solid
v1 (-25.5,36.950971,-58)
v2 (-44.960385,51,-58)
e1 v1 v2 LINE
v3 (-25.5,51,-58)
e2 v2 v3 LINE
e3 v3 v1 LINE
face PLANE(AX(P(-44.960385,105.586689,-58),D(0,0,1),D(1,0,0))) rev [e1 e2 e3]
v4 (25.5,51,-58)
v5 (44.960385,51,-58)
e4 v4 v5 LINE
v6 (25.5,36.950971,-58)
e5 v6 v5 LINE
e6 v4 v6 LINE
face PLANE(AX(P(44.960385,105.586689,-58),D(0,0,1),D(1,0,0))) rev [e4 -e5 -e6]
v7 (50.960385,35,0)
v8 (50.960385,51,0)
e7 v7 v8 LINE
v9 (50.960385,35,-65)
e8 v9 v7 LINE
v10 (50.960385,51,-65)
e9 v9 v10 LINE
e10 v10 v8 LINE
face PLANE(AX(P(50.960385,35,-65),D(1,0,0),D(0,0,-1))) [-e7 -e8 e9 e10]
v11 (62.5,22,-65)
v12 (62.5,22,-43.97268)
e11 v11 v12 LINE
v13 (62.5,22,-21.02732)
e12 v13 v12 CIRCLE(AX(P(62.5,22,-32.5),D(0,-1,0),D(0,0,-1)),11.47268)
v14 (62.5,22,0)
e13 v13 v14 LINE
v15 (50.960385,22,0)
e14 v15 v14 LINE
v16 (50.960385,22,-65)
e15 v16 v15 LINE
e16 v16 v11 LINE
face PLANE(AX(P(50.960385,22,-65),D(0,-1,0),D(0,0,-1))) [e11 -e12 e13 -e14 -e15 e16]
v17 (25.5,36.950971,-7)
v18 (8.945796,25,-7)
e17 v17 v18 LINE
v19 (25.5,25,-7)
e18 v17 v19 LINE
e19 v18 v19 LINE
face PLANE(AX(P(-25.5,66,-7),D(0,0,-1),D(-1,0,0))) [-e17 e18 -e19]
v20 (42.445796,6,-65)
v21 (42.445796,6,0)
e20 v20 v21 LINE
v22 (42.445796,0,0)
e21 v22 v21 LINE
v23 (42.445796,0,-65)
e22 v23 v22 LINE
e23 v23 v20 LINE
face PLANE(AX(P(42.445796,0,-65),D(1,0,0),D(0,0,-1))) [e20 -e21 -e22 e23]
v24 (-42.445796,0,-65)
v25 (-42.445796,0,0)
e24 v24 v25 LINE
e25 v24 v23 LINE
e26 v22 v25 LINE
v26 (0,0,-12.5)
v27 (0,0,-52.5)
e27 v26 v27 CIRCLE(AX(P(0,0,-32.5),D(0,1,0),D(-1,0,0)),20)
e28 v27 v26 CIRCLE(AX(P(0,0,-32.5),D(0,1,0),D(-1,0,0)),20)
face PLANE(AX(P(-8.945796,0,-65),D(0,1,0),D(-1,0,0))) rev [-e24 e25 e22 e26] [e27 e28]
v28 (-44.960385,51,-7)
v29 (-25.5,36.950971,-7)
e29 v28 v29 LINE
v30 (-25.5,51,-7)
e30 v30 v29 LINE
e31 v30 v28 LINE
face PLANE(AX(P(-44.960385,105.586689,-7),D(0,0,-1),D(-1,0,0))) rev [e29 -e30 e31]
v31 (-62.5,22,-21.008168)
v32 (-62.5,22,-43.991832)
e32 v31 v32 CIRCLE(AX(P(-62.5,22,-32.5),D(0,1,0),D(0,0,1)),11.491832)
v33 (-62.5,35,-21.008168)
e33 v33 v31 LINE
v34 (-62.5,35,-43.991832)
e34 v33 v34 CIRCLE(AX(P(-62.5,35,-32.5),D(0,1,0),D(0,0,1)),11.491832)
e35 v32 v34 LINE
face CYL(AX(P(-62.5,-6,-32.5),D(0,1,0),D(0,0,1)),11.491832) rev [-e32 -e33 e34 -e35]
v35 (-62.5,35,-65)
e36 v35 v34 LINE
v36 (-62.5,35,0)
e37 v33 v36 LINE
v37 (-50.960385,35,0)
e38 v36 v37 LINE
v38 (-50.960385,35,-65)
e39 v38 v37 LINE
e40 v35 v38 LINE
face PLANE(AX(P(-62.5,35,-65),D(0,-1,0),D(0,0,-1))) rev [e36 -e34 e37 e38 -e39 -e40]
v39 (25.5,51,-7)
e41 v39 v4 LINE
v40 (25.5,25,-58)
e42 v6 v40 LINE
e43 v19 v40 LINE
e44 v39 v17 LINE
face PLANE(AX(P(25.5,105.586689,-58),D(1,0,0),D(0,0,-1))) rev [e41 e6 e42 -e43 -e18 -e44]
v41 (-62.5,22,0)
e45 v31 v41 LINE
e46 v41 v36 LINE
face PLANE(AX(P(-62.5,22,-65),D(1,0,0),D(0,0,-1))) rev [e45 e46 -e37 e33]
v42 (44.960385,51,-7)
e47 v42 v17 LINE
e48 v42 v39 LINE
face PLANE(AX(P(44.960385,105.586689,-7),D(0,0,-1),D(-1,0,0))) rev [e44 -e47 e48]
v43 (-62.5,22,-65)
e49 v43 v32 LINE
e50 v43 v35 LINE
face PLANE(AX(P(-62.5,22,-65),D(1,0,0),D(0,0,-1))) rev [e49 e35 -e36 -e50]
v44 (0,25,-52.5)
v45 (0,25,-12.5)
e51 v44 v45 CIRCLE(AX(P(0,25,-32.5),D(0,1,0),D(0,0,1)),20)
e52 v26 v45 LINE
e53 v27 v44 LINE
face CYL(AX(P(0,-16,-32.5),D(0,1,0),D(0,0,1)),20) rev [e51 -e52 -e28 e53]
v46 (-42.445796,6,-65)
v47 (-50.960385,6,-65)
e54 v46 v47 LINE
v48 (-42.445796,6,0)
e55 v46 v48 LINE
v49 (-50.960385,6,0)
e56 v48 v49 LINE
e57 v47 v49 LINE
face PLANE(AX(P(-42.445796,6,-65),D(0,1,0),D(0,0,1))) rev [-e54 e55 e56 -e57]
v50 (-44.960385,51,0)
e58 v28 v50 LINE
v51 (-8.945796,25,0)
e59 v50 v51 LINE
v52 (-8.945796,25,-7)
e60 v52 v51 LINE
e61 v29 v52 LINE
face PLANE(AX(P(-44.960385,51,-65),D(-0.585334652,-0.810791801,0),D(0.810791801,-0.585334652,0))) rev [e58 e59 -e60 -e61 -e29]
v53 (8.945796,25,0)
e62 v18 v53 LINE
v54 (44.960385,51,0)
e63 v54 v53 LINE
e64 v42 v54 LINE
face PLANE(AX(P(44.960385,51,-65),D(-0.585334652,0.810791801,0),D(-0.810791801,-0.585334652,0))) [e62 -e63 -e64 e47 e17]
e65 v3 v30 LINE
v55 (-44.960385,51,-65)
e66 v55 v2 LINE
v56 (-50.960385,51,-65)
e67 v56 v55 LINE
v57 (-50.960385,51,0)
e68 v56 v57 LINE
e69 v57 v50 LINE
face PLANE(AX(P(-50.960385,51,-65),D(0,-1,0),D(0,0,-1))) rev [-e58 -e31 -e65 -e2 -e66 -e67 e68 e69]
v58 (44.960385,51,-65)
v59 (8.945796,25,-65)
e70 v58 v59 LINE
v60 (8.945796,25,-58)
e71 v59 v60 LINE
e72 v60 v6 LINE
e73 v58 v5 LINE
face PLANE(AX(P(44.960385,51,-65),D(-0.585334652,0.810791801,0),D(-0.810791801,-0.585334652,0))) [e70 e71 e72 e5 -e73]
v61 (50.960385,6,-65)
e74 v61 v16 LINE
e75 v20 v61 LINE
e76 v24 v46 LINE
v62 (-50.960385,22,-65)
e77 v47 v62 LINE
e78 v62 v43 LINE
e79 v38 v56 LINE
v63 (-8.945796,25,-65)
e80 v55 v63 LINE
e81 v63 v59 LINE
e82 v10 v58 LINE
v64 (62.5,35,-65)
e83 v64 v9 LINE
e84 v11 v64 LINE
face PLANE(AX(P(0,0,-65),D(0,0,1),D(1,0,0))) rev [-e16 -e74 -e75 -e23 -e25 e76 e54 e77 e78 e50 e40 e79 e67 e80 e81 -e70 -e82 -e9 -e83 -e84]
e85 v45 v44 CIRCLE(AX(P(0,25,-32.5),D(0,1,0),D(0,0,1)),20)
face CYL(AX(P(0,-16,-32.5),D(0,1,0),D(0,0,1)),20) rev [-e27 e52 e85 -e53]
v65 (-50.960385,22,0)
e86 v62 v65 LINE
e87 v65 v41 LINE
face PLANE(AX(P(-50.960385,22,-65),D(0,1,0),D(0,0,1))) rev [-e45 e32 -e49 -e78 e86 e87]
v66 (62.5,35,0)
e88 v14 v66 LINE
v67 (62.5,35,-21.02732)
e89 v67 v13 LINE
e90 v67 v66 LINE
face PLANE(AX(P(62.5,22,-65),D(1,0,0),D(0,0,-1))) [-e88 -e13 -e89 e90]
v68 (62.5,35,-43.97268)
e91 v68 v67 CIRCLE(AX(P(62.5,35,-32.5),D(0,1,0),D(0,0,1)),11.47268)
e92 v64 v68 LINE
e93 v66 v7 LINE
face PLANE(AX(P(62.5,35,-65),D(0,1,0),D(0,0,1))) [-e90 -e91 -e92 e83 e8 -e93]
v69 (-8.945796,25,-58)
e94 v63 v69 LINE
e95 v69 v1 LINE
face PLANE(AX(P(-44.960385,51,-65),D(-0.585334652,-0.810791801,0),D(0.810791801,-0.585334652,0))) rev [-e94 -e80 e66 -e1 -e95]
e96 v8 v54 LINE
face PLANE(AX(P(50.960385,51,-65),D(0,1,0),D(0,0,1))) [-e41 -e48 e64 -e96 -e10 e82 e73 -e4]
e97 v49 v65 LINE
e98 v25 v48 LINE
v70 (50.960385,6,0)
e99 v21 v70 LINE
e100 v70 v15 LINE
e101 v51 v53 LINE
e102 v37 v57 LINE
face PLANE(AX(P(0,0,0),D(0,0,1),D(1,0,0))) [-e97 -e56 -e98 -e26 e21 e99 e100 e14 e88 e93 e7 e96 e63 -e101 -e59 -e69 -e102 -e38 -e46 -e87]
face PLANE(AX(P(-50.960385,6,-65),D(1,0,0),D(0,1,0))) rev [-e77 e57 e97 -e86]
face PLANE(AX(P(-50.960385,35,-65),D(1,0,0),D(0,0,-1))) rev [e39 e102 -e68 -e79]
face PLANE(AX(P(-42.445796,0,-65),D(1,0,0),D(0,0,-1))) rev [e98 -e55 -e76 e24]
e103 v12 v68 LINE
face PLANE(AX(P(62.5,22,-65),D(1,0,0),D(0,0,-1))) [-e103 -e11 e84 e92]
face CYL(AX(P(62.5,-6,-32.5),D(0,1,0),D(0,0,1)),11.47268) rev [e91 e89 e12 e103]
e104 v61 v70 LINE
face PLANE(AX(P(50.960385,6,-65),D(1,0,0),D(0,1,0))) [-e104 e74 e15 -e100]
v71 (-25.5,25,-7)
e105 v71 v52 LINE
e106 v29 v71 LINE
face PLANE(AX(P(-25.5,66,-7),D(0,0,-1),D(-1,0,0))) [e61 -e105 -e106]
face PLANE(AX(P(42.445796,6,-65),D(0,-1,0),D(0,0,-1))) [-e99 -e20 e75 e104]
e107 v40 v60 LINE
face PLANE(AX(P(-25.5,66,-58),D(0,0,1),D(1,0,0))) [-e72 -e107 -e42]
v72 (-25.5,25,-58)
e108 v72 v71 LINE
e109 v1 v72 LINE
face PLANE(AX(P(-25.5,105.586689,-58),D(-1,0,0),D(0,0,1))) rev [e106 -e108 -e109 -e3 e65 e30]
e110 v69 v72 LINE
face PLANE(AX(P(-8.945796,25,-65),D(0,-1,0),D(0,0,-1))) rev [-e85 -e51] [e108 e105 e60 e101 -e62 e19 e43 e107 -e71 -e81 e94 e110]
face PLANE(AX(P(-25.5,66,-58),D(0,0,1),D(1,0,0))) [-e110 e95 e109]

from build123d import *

# Parameters (mm, degrees)
STEPPED_CRADLE_BLOCK_65_DEPTH = 65
RAISED_BOSS_SKETCH_W          = 19.460384675
RAISED_BOSS_SKETCH_H          = 51
RAISED_BOSS_DEPTH             = 26
CRADLE_SLOT_SKETCH_W          = 51
CRADLE_SLOT_SKETCH_H          = 51
CRADLE_SLOT_CUT_DEPTH         = 41
CENTER_HOLE_SKETCH_R          = 20
CENTER_HOLE_40_DEPTH          = 41
FRONT_RELIEF_SKETCH_R         = 11.472679984
FRONT_RELIEF_SKETCH_R_2       = 11.491831568
FRONT_RELIEF_CUT_DEPTH        = 41


with BuildPart() as part:
    # Stepped Cradle Profile Sketch → Stepped Cradle Block 65 (new body)
    with BuildSketch(Plane.XY):
        Polygon((-42.445795816, 0), (-42.445795816, 6), (-50.960384675, 6), (-50.960384675, 22), (-62.5, 22), (-62.5, 35), (-50.960384675, 35), (-50.960384675, 51), (-44.960384675, 51), (-8.945795816, 25), (8.945795816, 25), (44.960384675, 51), (50.960384675, 51), (50.960384675, 35), (62.5, 35), (62.5, 22), (50.960384675, 22), (50.960384675, 6), (42.445795816, 6), (42.445795816, 0), (8.945795816, 0), (-8.945795816, 0), align=None)
    extrude(amount=-STEPPED_CRADLE_BLOCK_65_DEPTH)

    # Raised Boss Sketch → Raised Boss (add)
    with BuildSketch(Plane(origin=(0, 25, 0), x_dir=(1, 0, 0), z_dir=(0, 1, 0))):
        with Locations((-35.230192338, 32.5)):
            Rectangle(RAISED_BOSS_SKETCH_W, RAISED_BOSS_SKETCH_H)
        with Locations((35.230192338, 32.5)):
            Rectangle(RAISED_BOSS_SKETCH_W, RAISED_BOSS_SKETCH_H)
    extrude(amount=RAISED_BOSS_DEPTH)

    # Cradle Slot Sketch → Cradle Slot Cut (cut)
    with BuildSketch(Plane(origin=(0, 25, 0), x_dir=(1, 0, 0), z_dir=(0, 1, 0))):
        with Locations((0, 32.5)):
            Rectangle(CRADLE_SLOT_SKETCH_W, CRADLE_SLOT_SKETCH_H)
    extrude(amount=CRADLE_SLOT_CUT_DEPTH, mode=Mode.SUBTRACT)

    # Center Hole Sketch → Center Hole Ø40 (cut)
    with BuildSketch(Plane(origin=(0, 25, 0), x_dir=(1, 0, 0), z_dir=(0, 1, 0))):
        with Locations(Location((0, 32.5, 0), (0, 0, 270))):
            Circle(CENTER_HOLE_SKETCH_R)
    extrude(amount=-CENTER_HOLE_40_DEPTH, mode=Mode.SUBTRACT)

    # Front Relief Sketch → Front Relief Cut (cut)
    with BuildSketch(Plane(origin=(0, 35, 0), x_dir=(1, 0, 0), z_dir=(0, 1, 0))):
        with Locations((62.5, 32.5)):
            Circle(FRONT_RELIEF_SKETCH_R)
        with Locations((-62.5, 32.5)):
            Circle(FRONT_RELIEF_SKETCH_R_2)
    extrude(amount=-FRONT_RELIEF_CUT_DEPTH, mode=Mode.SUBTRACT)


solid = part.part
